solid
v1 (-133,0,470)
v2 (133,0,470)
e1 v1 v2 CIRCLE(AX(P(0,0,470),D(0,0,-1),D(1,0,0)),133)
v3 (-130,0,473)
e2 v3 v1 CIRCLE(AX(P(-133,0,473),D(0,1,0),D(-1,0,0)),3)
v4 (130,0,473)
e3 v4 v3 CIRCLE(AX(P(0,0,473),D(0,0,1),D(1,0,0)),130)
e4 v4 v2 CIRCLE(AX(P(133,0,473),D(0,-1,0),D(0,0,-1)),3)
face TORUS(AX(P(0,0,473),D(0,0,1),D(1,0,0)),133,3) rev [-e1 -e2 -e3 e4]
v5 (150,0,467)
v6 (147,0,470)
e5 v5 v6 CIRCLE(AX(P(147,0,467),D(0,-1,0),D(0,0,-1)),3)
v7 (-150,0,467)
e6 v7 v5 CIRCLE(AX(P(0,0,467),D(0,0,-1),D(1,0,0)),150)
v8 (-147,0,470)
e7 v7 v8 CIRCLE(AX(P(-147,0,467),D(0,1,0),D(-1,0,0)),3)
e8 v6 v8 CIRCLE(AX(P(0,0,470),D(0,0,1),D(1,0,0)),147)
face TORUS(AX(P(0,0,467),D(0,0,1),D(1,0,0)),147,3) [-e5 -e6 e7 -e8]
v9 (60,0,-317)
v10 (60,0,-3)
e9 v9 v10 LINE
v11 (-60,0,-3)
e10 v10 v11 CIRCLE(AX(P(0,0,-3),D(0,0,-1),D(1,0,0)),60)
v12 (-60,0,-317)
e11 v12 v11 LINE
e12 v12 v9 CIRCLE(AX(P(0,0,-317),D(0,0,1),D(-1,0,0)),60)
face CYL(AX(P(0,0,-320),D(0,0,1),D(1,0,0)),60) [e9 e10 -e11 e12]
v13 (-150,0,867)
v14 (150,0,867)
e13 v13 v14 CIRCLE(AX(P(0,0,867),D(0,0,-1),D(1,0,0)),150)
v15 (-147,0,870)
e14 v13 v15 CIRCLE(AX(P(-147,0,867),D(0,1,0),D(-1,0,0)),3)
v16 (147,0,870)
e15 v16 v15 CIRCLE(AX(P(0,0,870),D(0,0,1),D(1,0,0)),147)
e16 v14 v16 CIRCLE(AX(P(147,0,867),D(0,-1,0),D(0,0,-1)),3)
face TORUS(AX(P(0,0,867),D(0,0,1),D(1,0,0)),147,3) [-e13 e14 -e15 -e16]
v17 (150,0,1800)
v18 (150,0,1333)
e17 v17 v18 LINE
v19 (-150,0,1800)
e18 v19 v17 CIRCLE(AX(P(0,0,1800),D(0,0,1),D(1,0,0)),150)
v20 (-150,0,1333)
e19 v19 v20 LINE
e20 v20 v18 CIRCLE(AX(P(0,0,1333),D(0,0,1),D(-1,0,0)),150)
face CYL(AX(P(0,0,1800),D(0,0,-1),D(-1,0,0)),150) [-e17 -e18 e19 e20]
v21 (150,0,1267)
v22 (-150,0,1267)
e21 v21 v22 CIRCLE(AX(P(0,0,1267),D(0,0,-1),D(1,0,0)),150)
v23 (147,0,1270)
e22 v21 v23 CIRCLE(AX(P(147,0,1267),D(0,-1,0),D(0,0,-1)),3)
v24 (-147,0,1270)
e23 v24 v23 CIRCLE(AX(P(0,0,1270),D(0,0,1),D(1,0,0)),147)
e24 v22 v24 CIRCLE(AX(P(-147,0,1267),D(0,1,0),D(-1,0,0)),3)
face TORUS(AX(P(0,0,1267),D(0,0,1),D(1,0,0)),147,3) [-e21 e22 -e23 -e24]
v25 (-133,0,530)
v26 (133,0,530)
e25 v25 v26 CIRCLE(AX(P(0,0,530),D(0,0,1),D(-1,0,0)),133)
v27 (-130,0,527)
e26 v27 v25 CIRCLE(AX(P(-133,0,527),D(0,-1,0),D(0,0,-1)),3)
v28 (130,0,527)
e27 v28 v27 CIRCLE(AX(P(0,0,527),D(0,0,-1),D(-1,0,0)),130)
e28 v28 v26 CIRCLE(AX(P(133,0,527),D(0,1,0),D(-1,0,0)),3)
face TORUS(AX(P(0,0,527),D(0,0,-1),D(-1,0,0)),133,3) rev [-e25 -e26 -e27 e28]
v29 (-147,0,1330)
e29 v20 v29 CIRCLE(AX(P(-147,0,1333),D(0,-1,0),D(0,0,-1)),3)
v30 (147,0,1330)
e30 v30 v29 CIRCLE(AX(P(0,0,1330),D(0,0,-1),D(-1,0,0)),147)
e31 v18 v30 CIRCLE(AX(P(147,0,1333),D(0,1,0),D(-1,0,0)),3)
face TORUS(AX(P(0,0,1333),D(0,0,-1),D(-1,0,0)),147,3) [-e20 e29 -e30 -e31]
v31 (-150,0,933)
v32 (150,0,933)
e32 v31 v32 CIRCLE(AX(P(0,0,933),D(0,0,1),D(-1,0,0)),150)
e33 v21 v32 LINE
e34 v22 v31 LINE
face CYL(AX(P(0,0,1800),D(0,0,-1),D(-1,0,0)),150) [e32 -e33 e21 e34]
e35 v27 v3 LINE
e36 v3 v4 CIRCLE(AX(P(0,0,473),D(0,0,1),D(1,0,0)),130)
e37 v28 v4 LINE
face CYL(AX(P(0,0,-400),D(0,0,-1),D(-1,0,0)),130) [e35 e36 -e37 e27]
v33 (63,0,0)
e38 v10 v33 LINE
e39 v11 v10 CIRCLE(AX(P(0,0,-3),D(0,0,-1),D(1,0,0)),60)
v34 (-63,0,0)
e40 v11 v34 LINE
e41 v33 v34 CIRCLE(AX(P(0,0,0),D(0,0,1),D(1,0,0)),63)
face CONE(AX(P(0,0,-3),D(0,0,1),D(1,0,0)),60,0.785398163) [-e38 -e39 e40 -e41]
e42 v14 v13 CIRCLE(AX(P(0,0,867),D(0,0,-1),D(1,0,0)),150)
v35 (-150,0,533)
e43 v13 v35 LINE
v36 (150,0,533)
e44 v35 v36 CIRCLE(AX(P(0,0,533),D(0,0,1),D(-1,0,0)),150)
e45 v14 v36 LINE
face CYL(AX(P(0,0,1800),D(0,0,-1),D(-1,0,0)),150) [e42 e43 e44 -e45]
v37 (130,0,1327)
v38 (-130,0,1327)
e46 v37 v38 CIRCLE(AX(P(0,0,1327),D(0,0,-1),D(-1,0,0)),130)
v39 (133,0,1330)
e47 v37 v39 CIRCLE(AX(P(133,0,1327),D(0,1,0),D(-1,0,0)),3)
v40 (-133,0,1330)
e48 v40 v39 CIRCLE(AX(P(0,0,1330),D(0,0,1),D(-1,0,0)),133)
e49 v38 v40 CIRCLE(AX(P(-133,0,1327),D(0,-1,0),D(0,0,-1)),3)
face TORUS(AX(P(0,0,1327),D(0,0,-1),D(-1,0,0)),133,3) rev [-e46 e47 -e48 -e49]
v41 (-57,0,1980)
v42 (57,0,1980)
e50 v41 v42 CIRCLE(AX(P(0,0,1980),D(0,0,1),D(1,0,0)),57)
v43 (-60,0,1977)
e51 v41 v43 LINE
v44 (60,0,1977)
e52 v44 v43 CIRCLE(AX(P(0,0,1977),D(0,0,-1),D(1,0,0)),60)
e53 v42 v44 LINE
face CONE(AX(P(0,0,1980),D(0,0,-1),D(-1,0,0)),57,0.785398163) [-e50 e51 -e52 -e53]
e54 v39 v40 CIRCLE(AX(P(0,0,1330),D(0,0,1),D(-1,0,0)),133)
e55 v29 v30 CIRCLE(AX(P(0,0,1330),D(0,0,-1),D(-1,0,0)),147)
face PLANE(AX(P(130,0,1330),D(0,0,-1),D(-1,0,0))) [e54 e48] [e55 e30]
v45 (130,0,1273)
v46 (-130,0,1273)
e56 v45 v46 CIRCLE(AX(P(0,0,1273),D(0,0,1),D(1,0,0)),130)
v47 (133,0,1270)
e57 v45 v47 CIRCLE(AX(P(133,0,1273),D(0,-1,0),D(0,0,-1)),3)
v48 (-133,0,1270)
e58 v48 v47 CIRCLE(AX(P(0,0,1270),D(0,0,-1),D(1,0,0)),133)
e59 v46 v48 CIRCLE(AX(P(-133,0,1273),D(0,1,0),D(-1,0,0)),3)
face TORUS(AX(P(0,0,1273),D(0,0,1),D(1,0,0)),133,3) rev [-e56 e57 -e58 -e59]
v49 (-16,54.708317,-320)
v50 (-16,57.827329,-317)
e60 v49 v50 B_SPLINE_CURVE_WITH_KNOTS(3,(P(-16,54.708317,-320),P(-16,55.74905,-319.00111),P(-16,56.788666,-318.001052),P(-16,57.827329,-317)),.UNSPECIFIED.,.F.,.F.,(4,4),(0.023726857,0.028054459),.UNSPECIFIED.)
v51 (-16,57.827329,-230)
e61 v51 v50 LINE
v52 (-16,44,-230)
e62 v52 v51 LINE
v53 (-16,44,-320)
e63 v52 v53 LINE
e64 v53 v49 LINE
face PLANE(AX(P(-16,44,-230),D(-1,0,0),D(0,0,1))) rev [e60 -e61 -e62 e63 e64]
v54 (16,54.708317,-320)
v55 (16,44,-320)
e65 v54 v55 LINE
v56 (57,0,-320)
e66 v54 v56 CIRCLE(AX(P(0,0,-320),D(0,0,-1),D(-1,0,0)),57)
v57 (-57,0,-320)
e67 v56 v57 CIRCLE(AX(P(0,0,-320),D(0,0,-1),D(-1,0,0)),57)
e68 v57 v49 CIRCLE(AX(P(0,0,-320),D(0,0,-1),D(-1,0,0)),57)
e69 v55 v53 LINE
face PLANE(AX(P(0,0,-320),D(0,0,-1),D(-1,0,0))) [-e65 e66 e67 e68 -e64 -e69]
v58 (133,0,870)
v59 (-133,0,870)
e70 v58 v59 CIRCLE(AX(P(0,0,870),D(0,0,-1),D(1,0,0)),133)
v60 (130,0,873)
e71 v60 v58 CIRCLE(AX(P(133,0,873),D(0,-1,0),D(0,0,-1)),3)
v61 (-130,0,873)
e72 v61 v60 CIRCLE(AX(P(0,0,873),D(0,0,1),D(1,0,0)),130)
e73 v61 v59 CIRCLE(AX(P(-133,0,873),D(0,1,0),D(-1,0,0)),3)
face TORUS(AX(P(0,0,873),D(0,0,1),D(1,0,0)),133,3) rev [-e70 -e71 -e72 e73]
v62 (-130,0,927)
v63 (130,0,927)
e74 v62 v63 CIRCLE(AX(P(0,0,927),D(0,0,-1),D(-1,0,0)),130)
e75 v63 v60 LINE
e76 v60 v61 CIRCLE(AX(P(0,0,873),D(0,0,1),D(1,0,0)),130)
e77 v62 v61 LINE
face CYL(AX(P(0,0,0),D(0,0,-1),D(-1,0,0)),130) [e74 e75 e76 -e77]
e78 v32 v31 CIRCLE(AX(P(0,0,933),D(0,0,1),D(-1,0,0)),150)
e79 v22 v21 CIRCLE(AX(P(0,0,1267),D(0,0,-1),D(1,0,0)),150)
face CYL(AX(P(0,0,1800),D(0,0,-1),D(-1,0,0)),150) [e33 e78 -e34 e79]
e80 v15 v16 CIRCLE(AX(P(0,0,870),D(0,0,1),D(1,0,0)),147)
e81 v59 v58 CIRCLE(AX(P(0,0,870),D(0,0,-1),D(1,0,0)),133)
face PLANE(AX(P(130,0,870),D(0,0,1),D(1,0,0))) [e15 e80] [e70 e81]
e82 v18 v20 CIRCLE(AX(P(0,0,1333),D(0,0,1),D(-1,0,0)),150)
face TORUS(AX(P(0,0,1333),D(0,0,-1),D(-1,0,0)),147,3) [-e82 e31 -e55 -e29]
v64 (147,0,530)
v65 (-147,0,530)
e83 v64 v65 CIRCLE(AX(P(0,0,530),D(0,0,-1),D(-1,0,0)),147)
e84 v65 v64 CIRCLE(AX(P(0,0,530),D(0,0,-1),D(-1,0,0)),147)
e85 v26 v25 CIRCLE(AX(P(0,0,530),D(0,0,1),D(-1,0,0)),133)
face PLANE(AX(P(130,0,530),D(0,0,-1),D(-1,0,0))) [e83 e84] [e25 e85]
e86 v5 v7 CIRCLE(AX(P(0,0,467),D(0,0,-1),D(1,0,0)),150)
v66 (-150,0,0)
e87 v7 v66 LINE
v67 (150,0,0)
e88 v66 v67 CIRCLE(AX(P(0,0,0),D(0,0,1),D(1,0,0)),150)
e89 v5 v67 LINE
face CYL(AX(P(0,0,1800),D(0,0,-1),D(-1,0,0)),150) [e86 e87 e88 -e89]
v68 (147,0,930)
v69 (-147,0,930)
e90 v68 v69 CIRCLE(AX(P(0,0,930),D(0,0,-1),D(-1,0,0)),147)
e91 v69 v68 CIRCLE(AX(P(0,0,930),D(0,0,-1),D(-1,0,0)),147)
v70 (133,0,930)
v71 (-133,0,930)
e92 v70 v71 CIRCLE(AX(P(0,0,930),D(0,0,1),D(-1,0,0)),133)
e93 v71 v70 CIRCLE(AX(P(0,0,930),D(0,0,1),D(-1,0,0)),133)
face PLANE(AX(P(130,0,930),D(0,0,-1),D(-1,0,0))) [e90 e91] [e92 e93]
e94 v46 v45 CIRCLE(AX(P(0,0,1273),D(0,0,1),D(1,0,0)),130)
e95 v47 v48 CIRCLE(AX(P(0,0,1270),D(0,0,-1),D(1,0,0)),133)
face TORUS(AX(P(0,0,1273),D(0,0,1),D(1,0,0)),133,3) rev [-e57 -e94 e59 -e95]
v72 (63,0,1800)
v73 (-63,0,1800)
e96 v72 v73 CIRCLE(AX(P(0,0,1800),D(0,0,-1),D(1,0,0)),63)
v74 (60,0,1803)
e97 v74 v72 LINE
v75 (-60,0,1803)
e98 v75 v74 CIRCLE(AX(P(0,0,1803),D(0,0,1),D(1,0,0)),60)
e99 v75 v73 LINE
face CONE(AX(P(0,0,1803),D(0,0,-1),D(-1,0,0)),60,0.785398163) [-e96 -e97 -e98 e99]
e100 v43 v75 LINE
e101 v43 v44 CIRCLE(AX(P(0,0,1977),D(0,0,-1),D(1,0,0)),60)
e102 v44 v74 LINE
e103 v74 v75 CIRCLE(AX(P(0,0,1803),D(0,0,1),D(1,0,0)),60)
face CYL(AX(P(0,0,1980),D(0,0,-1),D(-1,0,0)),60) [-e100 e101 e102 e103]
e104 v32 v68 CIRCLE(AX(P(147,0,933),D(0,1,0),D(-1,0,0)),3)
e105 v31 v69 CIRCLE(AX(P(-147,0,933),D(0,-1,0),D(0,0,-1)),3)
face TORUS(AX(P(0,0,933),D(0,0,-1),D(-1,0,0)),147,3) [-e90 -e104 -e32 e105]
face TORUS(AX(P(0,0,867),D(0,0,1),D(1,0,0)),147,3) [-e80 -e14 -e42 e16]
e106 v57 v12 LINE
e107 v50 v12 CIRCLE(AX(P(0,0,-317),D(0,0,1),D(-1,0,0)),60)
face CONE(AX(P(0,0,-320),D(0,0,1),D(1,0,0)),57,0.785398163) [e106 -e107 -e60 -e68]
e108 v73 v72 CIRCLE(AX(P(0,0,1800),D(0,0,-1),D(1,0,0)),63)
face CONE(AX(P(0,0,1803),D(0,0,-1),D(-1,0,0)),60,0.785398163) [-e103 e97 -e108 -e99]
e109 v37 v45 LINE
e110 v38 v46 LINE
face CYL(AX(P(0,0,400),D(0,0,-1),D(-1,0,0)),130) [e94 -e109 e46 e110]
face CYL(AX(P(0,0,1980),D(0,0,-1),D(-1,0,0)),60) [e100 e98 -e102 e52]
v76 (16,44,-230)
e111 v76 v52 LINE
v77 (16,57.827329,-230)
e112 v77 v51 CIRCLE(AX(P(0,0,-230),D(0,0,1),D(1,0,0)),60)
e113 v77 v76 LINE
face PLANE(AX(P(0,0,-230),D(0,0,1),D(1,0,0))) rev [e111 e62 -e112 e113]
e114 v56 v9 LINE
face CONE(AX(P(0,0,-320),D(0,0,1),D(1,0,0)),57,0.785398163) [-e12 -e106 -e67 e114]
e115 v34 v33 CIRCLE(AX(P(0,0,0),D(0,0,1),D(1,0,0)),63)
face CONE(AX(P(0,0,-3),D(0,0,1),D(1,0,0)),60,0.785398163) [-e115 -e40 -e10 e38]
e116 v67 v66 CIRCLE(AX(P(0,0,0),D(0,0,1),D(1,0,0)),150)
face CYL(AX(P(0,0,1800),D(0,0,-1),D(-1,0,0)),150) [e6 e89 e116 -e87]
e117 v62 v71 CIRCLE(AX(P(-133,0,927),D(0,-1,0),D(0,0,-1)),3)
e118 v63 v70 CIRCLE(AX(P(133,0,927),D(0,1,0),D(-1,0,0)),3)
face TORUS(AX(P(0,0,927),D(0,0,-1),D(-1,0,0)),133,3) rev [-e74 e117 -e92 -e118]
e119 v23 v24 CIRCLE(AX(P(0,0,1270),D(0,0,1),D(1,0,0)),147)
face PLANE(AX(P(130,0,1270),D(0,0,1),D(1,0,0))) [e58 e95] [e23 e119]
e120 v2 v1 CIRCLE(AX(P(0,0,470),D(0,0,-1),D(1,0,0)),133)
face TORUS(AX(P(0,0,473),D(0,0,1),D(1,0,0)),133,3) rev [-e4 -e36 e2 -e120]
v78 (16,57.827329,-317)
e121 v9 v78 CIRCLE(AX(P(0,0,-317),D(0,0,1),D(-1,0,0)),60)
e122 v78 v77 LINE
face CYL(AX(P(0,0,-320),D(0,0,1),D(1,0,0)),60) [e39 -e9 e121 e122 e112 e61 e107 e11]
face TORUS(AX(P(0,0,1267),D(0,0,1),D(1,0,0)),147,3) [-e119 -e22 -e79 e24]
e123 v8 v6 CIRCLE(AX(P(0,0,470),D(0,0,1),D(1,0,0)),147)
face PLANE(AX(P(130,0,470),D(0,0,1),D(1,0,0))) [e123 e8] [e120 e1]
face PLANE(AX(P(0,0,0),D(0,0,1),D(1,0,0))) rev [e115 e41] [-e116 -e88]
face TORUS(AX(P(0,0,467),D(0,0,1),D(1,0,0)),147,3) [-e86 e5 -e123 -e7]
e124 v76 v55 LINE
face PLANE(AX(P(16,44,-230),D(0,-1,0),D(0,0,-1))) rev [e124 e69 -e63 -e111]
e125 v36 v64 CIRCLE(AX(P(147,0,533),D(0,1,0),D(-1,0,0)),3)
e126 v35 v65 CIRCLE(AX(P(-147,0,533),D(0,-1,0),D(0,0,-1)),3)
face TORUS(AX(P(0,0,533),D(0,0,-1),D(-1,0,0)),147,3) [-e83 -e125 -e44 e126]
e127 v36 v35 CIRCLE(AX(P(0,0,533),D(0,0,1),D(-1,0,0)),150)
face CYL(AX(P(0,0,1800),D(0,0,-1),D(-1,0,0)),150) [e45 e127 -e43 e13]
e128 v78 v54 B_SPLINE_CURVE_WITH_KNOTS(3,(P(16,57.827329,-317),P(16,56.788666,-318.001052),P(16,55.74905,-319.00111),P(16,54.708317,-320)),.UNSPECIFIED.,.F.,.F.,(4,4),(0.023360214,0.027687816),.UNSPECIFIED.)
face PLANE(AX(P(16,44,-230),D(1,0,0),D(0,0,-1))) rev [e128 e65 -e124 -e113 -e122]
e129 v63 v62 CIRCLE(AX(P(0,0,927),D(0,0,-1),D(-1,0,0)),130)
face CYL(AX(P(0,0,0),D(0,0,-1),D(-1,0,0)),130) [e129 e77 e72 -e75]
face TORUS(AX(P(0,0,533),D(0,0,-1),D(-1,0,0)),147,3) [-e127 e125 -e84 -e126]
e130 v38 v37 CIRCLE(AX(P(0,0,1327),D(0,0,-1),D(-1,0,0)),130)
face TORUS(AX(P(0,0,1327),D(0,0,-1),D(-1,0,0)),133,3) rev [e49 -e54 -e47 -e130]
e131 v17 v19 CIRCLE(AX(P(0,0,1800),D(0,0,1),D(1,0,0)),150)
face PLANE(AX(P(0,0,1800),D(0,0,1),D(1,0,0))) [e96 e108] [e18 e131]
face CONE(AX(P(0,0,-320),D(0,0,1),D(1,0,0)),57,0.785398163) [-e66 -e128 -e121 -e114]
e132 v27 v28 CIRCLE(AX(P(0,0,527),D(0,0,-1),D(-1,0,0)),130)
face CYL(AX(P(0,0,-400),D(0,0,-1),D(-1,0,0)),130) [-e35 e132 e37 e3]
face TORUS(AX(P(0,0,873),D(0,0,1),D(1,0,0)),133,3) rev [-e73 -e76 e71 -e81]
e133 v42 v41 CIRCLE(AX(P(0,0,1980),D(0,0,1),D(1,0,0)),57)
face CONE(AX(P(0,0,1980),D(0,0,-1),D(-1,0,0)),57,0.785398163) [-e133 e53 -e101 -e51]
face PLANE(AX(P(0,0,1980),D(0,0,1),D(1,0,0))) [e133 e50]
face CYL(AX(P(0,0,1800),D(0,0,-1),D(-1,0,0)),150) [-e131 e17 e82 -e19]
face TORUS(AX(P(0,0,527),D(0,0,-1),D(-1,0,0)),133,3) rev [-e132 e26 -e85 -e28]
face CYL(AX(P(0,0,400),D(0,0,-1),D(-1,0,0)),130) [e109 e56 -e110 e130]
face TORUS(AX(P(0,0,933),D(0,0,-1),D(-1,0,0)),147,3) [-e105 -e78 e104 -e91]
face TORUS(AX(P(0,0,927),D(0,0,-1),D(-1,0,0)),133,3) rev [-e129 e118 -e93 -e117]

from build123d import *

# Parameters (mm, degrees)
SKETCH1_R                  = 150
BOSS_EXTRUDE1_DEPTH        = 1800
SKETCH2_W                  = 40
SKETCH2_H                  = 60
FILLET1_R                  = 3
LPATTERN1_COUNT            = 2
LPATTERN1_PITCH            = 400
FILLET1_OF_LPATTERN1_R     = 3
LPATTERN1_COL_COUNT        = 2
LPATTERN1_COL_PITCH        = 400
FILLET1_OF_LPATTERN1_COL_R = 3
SKETCH3_R                  = 60
BOSS_EXTRUDE2_DEPTH        = 180
CHAMFER1_SIZE              = 3
BOSS_EXTRUDE3_START        = 320
SKETCH4_R                  = 60
BOSS_EXTRUDE3_DEPTH        = 320
CHAMFER2_SIZE              = 3
SKETCH5_W                  = 32
SKETCH5_H                  = 32
CUT_EXTRUDE1_DEPTH         = 90


with BuildPart() as part:
    # Sketch1 → Boss-Extrude1 (new body)
    with BuildSketch(Plane.XY):
        Circle(SKETCH1_R)
    extrude(amount=BOSS_EXTRUDE1_DEPTH)

    # Sketch2 → Cut-Revolve1 (revolve, cut)
    with BuildSketch(Plane(origin=(0, 0, 0), x_dir=(1, 0, 0), z_dir=(0, 1, 0)), mode=Mode.PRIVATE) as cut_revolve1_sk:
        with Locations((150, -900)):
            Rectangle(SKETCH2_W, SKETCH2_H)
    cut_revolve1 = revolve(cut_revolve1_sk.sketch.rotate(Axis((0, 0, 0), (0, 0, 1)), 180), axis=Axis((0, 0, 0), (0, 0, 1)), mode=Mode.SUBTRACT)

    # Fillet1
    fillet1_edges = [part.edges().sort_by_distance(p)[0] for p in [
        (130, 0, 930),
        (-150, 0, 930),
        (130, 0, 870),
        (-150, 0, 870),
    ]]
    fillet(fillet1_edges, radius=FILLET1_R)

    # LPattern1: Cut-Revolve1 ×2
    with Locations(*[(0, 0, -i * LPATTERN1_PITCH) for i in range(1, LPATTERN1_COUNT)]):
        add(cut_revolve1, mode=Mode.SUBTRACT)

    # Fillet1 of LPattern1
    fillet1_of_lpattern1_edges = [part.edges().sort_by_distance(p)[0] for p in [
        (130, 0, 530),
        (-150, 0, 530),
        (130, 0, 470),
        (-150, 0, 470),
    ]]
    fillet(fillet1_of_lpattern1_edges, radius=FILLET1_OF_LPATTERN1_R)

    # LPattern1 col: Cut-Revolve1 ×2
    with Locations(*[(0, 0, i * LPATTERN1_COL_PITCH) for i in range(1, LPATTERN1_COL_COUNT)]):
        add(cut_revolve1, mode=Mode.SUBTRACT)

    # Fillet1 of LPattern1 col
    fillet1_of_lpattern1_col_edges = [part.edges().sort_by_distance(p)[0] for p in [
        (130, 0, 1330),
        (-150, 0, 1330),
        (130, 0, 1270),
        (-150, 0, 1270),
    ]]
    fillet(fillet1_of_lpattern1_col_edges, radius=FILLET1_OF_LPATTERN1_COL_R)

    # Sketch3 → Boss-Extrude2 (add)
    with BuildSketch(Plane.XY.offset(1800)):
        Circle(SKETCH3_R)
    extrude(amount=BOSS_EXTRUDE2_DEPTH)

    # Chamfer1
    chamfer1_edges = [part.edges().sort_by_distance(p)[0] for p in [
        (-60, 0, 1800),
        (-60, 0, 1980),
    ]]
    chamfer(chamfer1_edges, length=CHAMFER1_SIZE)

    # Sketch4 → Boss-Extrude3 (add)
    with BuildSketch(Plane(origin=(0, 0, 0), x_dir=(-1, 0, 0), z_dir=(0, 0, -1)).offset(BOSS_EXTRUDE3_START)):
        with Locations(Location((0, 0, 0), (0, 0, 180))):
            Circle(SKETCH4_R)
    extrude(amount=-BOSS_EXTRUDE3_DEPTH)

    # Chamfer2
    chamfer2_edges = [part.edges().sort_by_distance(p)[0] for p in [
        (-60, 0, 0),
        (-60, 0, -320),
    ]]
    chamfer(chamfer2_edges, length=CHAMFER2_SIZE)

    # Sketch5 → Cut-Extrude1 (cut)
    with BuildSketch(Plane(origin=(0, 0, -320), x_dir=(-1, 0, 0), z_dir=(0, 0, -1))):
        with Locations((0, 60)):
            Rectangle(SKETCH5_W, SKETCH5_H)
    extrude(amount=-CUT_EXTRUDE1_DEPTH, mode=Mode.SUBTRACT)


solid = part.part
